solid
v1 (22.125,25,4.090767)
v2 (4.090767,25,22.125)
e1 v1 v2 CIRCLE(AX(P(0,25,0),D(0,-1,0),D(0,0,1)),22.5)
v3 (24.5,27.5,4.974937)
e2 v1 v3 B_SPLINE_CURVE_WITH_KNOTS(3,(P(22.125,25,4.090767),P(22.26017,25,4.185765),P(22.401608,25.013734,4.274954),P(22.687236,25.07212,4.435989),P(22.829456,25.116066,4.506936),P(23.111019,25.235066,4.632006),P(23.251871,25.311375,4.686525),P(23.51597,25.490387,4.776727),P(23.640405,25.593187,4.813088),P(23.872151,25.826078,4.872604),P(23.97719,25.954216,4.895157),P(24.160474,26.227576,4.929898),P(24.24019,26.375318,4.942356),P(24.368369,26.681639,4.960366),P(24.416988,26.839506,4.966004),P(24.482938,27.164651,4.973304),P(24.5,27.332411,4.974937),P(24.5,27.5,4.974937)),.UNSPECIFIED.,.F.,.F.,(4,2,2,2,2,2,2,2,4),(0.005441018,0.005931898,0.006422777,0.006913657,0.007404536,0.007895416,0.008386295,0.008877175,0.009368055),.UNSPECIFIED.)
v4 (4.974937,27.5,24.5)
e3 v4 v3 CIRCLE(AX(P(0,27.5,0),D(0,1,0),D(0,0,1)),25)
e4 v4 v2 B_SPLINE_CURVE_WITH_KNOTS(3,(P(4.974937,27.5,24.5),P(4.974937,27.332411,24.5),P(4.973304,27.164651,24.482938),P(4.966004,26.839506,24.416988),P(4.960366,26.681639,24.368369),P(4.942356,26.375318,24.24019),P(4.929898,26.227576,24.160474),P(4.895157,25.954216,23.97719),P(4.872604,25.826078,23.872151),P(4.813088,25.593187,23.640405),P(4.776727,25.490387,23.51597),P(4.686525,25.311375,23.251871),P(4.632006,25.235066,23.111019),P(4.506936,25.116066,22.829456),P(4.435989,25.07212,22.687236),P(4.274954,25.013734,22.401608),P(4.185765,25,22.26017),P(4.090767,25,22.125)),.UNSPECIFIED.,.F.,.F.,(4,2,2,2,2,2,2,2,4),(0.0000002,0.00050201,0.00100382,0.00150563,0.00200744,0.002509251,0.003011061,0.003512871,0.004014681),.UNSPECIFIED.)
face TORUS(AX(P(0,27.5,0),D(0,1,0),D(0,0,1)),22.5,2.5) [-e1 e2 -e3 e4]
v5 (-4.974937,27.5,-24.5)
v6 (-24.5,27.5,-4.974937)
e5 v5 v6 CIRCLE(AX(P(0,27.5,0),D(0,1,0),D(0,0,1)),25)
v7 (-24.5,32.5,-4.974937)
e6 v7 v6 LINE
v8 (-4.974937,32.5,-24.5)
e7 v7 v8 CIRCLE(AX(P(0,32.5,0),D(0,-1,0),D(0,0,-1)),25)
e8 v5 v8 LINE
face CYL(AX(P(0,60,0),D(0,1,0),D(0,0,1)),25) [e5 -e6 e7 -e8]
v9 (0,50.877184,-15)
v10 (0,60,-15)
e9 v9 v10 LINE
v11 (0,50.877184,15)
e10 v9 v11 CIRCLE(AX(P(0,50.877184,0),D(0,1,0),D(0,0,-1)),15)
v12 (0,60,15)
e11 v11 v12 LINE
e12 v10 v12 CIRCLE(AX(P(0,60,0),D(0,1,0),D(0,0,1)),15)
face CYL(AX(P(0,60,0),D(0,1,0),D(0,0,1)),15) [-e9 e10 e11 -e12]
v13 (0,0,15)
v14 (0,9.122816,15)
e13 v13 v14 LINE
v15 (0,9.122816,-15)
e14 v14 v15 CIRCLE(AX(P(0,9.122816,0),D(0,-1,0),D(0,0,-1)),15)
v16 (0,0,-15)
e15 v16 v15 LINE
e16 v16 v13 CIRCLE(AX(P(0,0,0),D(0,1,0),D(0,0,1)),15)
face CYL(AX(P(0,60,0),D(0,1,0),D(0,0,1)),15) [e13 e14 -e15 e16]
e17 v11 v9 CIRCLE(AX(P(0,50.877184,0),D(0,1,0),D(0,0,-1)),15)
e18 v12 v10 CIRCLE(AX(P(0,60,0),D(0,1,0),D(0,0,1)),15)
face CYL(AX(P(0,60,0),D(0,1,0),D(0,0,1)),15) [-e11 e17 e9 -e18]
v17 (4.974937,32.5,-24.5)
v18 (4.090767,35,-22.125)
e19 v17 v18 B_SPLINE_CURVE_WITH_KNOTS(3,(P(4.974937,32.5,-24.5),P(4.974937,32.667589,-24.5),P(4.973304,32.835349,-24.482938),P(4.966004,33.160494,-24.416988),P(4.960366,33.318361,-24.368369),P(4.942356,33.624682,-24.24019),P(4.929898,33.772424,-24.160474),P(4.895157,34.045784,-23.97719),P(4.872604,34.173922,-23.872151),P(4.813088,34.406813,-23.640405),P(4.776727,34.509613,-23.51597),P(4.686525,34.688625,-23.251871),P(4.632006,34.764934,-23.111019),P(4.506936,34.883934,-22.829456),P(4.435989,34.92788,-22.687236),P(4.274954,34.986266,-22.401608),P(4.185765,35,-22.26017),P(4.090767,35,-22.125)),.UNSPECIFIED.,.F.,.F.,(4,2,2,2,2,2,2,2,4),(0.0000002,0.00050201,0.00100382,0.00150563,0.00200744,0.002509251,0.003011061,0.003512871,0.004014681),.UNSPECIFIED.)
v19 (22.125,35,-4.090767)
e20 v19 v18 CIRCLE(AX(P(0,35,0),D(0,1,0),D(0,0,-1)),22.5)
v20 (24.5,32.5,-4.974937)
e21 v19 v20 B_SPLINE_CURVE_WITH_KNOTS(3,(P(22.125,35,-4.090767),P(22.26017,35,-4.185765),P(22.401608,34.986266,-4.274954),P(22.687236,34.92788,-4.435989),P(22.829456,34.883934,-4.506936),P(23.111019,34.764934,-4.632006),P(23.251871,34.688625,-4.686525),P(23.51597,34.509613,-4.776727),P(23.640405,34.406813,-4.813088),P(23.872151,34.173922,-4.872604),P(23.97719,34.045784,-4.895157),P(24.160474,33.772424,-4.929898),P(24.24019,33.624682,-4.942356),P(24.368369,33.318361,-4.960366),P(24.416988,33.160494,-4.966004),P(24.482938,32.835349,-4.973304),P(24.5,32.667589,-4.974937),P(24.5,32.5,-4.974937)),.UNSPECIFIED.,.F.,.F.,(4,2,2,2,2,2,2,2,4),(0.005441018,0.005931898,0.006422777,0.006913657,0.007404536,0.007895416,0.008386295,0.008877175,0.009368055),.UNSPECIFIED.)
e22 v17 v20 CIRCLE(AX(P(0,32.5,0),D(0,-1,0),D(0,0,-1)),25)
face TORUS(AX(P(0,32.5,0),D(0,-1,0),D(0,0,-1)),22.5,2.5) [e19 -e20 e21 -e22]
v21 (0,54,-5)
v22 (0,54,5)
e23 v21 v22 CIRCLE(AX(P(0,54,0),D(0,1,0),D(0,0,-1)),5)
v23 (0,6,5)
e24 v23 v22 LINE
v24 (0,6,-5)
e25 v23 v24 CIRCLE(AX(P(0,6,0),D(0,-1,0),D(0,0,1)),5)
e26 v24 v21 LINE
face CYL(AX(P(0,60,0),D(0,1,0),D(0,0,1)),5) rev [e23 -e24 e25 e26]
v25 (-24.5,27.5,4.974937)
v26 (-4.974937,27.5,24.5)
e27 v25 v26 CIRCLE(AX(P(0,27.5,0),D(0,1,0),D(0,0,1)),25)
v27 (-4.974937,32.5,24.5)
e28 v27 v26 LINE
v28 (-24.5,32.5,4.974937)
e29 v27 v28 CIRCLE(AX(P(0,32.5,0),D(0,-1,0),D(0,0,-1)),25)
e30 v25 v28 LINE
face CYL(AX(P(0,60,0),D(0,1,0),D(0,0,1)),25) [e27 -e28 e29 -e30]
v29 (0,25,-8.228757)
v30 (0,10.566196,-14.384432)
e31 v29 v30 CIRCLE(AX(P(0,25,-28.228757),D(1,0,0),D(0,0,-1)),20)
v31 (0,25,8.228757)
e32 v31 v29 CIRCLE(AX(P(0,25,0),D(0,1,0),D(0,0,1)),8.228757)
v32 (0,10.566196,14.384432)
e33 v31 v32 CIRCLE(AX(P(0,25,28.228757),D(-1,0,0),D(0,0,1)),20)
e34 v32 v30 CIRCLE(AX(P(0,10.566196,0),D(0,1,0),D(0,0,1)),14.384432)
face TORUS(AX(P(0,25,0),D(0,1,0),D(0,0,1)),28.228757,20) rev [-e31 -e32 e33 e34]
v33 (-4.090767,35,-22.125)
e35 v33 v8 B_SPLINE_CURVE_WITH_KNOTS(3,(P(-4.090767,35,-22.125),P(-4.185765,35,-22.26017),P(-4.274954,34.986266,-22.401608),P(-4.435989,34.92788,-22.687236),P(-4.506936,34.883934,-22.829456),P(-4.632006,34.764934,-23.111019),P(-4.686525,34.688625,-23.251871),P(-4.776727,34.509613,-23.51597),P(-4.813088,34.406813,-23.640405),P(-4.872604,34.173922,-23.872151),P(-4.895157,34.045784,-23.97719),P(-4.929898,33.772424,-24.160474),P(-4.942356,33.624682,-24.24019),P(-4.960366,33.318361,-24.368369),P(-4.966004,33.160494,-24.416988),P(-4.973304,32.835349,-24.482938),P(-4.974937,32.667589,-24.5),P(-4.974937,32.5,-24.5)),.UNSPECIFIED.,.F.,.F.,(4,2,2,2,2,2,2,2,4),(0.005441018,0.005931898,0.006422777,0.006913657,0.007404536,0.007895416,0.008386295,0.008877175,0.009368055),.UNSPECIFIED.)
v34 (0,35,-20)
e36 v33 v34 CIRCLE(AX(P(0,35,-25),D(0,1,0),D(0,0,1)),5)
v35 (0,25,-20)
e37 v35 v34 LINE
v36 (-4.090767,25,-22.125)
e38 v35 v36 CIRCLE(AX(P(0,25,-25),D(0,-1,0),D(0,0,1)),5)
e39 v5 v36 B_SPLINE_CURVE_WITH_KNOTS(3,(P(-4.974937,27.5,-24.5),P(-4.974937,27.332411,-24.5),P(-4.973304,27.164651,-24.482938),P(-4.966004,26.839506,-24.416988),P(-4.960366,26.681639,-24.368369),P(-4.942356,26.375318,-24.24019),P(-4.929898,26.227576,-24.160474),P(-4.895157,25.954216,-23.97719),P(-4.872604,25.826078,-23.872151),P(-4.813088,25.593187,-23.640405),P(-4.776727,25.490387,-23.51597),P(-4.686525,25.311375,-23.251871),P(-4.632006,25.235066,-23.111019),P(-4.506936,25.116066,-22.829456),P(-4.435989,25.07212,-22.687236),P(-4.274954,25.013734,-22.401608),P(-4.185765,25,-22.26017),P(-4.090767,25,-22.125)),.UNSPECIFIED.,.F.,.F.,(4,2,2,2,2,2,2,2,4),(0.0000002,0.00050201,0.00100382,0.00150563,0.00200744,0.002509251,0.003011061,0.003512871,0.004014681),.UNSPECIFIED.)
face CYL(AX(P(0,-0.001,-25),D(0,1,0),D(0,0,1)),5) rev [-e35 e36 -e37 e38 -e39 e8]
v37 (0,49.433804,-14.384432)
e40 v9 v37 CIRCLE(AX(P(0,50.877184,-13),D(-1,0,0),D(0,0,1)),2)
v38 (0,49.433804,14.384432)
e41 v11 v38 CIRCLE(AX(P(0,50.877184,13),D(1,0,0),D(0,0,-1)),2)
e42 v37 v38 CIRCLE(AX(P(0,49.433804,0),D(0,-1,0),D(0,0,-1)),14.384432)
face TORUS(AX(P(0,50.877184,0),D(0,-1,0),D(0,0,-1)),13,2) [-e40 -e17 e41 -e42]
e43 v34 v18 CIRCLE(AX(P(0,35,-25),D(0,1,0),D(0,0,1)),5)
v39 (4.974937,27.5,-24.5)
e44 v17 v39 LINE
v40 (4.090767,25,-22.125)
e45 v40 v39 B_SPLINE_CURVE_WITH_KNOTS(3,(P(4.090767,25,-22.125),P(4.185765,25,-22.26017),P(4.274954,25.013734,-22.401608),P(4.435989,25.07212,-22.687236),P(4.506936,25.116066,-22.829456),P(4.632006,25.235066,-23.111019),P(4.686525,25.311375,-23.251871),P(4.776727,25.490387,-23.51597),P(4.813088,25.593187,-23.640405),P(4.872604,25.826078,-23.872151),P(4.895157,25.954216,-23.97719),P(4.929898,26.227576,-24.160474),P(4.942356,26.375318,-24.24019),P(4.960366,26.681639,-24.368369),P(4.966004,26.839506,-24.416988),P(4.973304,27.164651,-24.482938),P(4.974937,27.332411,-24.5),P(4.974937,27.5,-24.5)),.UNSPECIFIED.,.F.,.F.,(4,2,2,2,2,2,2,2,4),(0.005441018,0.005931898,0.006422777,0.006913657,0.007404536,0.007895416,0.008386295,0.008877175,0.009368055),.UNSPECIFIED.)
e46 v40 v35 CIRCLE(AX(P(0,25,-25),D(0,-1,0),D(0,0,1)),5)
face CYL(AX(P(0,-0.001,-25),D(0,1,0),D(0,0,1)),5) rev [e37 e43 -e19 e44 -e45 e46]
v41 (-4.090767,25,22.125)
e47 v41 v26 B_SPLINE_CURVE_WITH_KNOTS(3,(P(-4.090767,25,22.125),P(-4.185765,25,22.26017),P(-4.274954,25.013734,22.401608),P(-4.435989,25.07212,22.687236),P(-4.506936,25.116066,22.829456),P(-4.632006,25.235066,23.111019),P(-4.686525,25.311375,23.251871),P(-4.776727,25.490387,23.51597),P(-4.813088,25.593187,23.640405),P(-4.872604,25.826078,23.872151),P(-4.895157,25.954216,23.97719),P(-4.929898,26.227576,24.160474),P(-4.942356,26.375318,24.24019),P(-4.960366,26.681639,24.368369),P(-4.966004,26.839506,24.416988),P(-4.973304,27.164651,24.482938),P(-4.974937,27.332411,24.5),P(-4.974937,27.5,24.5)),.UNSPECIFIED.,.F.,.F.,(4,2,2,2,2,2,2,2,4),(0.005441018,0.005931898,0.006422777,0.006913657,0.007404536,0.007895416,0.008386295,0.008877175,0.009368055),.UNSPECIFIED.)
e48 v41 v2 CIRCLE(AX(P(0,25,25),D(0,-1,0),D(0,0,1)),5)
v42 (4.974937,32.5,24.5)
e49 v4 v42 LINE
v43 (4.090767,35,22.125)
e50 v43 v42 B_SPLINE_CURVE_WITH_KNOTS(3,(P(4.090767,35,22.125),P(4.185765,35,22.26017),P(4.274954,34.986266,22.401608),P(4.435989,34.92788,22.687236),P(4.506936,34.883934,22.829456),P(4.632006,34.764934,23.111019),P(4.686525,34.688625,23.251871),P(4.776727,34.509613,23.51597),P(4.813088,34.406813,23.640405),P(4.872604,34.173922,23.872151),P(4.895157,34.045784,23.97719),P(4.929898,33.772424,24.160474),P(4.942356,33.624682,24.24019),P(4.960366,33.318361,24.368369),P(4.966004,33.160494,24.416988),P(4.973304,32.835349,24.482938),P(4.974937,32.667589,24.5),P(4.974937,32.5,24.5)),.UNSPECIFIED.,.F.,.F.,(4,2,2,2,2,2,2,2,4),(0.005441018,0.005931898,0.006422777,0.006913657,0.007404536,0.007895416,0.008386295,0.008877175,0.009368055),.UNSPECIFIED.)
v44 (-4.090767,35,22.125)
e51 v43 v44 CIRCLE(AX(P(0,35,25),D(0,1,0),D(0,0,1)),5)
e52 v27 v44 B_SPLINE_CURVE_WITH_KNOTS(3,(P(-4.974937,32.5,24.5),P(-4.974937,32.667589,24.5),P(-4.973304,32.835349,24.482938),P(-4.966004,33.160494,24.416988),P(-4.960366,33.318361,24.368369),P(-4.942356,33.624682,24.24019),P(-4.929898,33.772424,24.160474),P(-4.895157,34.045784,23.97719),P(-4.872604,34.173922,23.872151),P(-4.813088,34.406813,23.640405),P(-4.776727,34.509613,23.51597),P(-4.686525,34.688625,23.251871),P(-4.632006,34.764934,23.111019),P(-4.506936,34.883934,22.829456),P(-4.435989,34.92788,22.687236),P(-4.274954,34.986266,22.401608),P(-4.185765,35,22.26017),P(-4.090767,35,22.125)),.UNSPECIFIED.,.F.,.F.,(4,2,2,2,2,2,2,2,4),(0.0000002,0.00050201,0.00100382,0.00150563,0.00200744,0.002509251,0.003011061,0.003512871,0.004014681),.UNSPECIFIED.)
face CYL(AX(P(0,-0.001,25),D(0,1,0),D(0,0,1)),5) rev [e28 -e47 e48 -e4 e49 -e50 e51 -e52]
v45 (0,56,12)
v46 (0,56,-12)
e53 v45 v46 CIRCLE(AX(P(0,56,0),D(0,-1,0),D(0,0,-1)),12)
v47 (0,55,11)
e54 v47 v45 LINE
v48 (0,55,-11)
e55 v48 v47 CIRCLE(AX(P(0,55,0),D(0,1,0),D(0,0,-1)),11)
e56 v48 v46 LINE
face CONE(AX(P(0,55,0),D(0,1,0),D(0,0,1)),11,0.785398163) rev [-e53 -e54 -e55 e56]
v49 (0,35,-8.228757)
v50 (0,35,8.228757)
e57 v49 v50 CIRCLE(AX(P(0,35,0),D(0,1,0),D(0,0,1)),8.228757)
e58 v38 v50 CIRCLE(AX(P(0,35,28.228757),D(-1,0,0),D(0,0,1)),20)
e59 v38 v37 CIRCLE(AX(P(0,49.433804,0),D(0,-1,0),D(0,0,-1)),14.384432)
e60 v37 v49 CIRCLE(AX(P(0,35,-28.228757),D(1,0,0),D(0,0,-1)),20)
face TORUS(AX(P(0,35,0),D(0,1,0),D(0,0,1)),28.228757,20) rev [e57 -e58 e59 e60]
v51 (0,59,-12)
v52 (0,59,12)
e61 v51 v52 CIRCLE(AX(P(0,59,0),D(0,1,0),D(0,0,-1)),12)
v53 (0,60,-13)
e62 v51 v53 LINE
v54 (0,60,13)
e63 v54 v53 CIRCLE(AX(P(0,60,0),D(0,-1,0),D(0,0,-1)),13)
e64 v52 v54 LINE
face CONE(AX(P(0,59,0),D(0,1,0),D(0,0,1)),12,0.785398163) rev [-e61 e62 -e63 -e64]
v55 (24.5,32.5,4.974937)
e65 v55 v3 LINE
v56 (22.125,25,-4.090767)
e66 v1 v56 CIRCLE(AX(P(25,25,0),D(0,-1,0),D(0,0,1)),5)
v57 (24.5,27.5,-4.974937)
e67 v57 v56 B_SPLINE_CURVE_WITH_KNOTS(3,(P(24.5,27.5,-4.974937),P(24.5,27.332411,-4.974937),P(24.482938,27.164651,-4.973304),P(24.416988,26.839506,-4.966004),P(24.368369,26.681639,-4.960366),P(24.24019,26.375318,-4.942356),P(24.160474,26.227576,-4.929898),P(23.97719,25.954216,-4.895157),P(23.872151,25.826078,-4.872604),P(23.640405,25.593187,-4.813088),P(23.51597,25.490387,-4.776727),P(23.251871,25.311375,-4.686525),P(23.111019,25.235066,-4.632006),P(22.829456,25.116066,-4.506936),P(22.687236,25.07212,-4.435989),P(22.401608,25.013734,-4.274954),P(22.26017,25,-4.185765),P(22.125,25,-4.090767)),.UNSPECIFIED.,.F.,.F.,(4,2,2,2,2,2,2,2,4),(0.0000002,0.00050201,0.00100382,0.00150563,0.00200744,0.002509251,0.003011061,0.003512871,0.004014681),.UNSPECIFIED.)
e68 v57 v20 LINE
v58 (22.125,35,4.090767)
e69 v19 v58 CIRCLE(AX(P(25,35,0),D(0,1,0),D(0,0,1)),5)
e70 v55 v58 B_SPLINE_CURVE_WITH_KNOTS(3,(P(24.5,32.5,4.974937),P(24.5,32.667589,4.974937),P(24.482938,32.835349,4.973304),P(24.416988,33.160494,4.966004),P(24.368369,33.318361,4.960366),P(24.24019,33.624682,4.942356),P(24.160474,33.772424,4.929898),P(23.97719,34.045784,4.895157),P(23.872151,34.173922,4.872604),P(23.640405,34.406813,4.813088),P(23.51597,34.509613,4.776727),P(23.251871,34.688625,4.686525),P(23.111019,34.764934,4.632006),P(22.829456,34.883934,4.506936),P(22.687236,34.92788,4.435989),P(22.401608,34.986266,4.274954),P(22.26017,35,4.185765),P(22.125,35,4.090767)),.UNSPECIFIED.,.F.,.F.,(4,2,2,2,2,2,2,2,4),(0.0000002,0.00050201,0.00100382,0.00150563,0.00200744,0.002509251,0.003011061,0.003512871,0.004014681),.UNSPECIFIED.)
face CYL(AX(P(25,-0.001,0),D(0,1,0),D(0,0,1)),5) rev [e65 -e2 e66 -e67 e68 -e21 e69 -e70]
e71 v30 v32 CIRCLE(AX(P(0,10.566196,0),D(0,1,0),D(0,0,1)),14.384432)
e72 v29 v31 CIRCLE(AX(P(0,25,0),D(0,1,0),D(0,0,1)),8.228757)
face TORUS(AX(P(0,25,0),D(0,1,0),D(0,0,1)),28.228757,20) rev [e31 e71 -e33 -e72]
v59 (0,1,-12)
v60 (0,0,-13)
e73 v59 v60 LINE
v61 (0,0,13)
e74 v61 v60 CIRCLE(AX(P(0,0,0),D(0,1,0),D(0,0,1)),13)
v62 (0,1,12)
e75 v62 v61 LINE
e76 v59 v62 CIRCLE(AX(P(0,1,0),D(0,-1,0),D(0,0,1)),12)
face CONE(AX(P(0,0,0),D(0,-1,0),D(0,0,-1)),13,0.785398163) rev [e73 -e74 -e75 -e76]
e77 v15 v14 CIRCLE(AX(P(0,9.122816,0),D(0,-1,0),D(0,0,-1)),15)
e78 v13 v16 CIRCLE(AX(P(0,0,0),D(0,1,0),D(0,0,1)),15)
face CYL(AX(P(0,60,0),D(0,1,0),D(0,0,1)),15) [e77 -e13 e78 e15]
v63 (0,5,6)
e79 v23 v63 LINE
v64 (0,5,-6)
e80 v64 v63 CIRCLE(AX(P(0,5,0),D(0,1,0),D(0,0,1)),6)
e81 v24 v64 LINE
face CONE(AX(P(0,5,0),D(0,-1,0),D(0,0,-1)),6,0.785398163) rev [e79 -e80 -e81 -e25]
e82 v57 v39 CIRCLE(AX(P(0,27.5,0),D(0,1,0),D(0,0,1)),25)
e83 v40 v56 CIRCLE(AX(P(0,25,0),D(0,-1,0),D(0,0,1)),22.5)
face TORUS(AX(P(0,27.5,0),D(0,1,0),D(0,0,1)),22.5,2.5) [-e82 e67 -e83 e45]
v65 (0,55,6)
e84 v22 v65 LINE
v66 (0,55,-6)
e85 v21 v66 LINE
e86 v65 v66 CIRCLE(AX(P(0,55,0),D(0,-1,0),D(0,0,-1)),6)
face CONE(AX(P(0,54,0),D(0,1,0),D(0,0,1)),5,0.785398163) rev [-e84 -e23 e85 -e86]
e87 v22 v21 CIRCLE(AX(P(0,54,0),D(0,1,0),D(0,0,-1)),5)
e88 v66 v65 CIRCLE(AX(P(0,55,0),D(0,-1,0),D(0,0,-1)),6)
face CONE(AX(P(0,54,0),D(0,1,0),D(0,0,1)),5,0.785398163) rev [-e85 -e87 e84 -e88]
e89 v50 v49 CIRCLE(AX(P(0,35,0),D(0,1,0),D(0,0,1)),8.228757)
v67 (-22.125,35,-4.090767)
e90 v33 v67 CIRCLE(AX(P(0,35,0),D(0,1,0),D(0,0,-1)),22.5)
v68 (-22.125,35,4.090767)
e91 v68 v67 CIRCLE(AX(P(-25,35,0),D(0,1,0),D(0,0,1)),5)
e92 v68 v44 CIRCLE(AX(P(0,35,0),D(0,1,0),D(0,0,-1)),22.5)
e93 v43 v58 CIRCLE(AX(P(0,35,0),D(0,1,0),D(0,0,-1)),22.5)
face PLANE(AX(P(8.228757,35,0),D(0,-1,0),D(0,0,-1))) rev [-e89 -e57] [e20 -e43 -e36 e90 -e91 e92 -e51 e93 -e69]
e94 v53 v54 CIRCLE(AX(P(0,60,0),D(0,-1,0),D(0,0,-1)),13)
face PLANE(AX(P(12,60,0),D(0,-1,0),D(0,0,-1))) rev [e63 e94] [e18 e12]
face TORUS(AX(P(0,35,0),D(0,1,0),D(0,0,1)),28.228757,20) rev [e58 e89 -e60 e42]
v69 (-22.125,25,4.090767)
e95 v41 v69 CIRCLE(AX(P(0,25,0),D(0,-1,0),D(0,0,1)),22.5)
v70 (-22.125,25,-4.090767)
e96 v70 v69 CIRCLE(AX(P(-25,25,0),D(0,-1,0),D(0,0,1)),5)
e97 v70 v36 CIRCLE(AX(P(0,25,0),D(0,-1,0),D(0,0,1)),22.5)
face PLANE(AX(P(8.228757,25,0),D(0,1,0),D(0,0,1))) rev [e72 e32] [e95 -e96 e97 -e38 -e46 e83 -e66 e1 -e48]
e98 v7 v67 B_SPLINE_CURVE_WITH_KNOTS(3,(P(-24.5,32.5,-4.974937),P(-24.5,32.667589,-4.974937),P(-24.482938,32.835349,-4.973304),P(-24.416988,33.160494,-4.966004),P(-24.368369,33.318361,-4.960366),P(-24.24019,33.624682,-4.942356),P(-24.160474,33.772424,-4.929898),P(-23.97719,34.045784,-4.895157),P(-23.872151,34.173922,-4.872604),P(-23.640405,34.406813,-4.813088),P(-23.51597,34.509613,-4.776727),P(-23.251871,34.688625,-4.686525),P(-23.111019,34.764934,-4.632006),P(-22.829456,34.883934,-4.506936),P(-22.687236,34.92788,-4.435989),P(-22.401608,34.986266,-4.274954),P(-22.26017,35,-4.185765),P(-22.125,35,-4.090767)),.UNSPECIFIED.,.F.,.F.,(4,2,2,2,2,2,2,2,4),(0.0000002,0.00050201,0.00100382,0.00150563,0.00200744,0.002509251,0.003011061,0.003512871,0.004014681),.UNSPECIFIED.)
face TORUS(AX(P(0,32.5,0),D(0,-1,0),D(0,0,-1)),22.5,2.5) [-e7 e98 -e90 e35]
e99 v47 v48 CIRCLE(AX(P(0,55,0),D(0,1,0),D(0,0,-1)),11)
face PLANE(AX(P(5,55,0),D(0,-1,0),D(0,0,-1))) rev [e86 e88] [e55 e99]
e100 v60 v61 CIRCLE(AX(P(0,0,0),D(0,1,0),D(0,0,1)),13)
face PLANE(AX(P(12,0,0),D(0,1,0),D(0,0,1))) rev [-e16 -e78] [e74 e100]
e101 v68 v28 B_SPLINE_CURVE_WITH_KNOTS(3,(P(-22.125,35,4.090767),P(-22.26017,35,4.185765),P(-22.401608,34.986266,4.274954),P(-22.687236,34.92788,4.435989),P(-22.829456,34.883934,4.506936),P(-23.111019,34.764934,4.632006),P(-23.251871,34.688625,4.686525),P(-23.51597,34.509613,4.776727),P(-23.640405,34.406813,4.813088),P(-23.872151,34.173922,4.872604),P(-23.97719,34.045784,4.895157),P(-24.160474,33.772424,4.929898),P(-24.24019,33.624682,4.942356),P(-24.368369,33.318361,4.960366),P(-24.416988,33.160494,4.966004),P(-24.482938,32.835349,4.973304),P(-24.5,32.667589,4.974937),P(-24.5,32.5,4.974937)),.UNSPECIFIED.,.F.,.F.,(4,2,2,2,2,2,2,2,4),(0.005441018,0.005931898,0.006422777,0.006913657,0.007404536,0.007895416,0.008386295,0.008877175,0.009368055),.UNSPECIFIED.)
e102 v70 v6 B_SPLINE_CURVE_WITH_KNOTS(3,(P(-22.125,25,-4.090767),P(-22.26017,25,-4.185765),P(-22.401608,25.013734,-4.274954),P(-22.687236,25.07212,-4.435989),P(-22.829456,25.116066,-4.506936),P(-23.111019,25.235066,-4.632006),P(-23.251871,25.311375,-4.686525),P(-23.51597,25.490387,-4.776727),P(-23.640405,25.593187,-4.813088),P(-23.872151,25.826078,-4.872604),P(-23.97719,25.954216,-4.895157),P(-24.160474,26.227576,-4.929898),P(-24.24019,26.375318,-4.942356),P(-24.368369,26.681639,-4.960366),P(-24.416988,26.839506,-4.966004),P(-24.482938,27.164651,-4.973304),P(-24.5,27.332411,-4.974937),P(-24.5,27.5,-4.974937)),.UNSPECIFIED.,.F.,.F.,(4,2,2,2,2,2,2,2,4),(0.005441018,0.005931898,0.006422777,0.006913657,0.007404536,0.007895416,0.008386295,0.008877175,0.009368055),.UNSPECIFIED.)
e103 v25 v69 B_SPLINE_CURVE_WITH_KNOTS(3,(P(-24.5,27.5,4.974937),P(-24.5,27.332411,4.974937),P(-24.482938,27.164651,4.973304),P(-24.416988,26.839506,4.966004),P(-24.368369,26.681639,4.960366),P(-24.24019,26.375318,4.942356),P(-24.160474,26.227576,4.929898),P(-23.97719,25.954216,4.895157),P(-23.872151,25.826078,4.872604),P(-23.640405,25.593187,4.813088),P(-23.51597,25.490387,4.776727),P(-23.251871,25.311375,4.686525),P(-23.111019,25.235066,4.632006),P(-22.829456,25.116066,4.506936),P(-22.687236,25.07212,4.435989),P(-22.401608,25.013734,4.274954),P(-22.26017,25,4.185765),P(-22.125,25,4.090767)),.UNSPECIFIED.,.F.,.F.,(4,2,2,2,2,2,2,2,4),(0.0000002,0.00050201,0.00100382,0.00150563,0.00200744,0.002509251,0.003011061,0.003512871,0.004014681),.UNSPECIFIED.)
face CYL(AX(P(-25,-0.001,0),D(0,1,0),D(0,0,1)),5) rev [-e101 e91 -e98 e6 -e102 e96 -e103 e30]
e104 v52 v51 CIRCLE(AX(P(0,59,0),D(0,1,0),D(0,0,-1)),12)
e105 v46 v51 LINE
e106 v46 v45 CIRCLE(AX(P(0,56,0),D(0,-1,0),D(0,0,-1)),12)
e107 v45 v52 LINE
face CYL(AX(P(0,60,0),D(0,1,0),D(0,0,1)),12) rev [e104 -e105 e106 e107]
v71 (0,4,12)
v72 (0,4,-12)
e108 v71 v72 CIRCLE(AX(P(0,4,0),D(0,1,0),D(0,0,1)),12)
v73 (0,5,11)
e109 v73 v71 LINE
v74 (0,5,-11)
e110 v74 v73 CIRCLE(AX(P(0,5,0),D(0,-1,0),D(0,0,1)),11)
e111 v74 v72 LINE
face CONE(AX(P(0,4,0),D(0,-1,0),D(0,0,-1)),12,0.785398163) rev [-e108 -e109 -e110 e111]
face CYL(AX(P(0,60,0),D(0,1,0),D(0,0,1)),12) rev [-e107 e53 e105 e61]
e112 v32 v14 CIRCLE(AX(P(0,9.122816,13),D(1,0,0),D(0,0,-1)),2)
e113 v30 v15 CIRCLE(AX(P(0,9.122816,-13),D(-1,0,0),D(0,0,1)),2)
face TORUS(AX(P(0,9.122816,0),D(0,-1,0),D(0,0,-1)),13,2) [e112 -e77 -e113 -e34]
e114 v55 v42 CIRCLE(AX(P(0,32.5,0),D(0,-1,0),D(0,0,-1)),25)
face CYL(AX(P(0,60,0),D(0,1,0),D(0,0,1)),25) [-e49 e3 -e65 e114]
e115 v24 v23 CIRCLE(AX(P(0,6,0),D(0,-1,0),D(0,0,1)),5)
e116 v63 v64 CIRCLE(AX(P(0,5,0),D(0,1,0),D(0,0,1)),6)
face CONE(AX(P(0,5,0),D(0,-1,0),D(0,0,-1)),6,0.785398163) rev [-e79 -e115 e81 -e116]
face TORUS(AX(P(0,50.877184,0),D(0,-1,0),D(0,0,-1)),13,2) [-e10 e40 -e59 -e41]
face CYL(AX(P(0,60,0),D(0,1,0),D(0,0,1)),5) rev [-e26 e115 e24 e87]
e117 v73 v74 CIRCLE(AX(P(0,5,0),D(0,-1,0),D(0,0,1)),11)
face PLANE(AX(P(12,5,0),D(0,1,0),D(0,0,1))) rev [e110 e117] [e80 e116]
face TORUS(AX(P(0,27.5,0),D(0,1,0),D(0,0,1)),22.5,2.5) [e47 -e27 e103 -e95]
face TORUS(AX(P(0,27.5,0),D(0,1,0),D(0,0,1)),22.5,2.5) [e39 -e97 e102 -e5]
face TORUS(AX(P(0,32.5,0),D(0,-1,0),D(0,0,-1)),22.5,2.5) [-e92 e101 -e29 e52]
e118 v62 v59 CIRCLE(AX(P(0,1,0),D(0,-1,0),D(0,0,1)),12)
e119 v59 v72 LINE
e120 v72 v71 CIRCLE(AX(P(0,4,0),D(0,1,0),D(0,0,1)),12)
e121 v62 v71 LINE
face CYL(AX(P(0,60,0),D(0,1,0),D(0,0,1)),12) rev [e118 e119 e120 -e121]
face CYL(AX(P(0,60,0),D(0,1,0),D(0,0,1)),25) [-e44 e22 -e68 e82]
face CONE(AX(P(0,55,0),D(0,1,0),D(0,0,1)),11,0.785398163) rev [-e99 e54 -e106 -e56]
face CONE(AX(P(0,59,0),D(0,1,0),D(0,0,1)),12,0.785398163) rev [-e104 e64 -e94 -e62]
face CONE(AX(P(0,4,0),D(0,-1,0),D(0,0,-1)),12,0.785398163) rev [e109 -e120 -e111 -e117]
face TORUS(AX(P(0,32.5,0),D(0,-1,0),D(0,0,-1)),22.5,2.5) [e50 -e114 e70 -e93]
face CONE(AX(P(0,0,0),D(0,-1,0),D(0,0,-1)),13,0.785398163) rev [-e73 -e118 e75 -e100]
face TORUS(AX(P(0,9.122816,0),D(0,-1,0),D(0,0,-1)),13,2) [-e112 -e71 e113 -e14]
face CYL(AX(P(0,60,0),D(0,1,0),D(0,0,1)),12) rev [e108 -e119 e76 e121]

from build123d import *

# Parameters (mm, degrees)
FLANGE_FILLET_R2_5_R     = 2.5
FLANGE_NOTCHES_4X_REACH  = 51.749
FLANGE_NOTCH_SKETCH_R    = 5
EDGE_CHAMFER_1X45_A_SIZE = 1
EDGE_FILLET_R2_R         = 2
EDGE_CHAMFER_1X45_B_SIZE = 1


with BuildPart() as part:
    # Hub Profile Sketch → Hub Body Revolve (revolve)
    with BuildSketch(Plane.XY, mode=Mode.PRIVATE) as hub_body_revolve_sk:
        with BuildLine():
            Line((12, 0), (12, 5))
            Line((12, 5), (5, 5))
            Line((5, 5), (5, 55))
            Line((5, 55), (12, 55))
            Line((12, 55), (12, 60))
            Line((12, 60), (15, 60))
            Line((15, 60), (15, 50))
            ThreePointArc((15, 50), (10, 43.228756555), (8.228756555, 35))
            Line((8.228756555, 35), (25, 35))
            Line((25, 35), (25, 25))
            Line((25, 25), (8.228756555, 25))
            ThreePointArc((8.228756555, 25), (10, 16.771243445), (15, 10))
            Line((15, 10), (15, 0))
            Line((15, 0), (12, 0))
        make_face()
    revolve(hub_body_revolve_sk.sketch.rotate(Axis((0, 60, 0), (0, -1, 0)), 90), axis=Axis((0, 60, 0), (0, -1, 0)))

    # Flange Fillet R2.5
    flange_fillet_r2_5_edges = [part.edges().sort_by_distance(p)[0] for p in [
        (0, 25, -25),
        (0, 35, -25),
    ]]
    fillet(flange_fillet_r2_5_edges, radius=FLANGE_FILLET_R2_5_R)

    # Flange Notch Sketch → Flange Notches 4x (cut, up to next)
    with BuildSketch(Plane(origin=(0, 35, 0), x_dir=(1, 0, 0), z_dir=(0, 1, 0)), mode=Mode.PRIVATE) as flange_notches_4x_sk1:
        with Locations((0, 25)):
            Circle(FLANGE_NOTCH_SKETCH_R)
    flange_notches_4x_tool1 = extrude(flange_notches_4x_sk1.sketch, amount=-FLANGE_NOTCHES_4X_REACH, mode=Mode.PRIVATE) & part.part
    # Flange Notch Sketch → Flange Notches 4x (cut, up to next)
    with BuildSketch(Plane(origin=(0, 35, 0), x_dir=(1, 0, 0), z_dir=(0, 1, 0)), mode=Mode.PRIVATE) as flange_notches_4x_sk2:
        with Locations((25, 0)):
            Circle(FLANGE_NOTCH_SKETCH_R)
    flange_notches_4x_tool2 = extrude(flange_notches_4x_sk2.sketch, amount=-FLANGE_NOTCHES_4X_REACH, mode=Mode.PRIVATE) & part.part
    # Flange Notch Sketch → Flange Notches 4x (cut, up to next)
    with BuildSketch(Plane(origin=(0, 35, 0), x_dir=(1, 0, 0), z_dir=(0, 1, 0)), mode=Mode.PRIVATE) as flange_notches_4x_sk3:
        with Locations((0, -25)):
            Circle(FLANGE_NOTCH_SKETCH_R)
    flange_notches_4x_tool3 = extrude(flange_notches_4x_sk3.sketch, amount=-FLANGE_NOTCHES_4X_REACH, mode=Mode.PRIVATE) & part.part
    # Flange Notch Sketch → Flange Notches 4x (cut, up to next)
    with BuildSketch(Plane(origin=(0, 35, 0), x_dir=(1, 0, 0), z_dir=(0, 1, 0)), mode=Mode.PRIVATE) as flange_notches_4x_sk4:
        with Locations((-25, 0)):
            Circle(FLANGE_NOTCH_SKETCH_R)
    flange_notches_4x_tool4 = extrude(flange_notches_4x_sk4.sketch, amount=-FLANGE_NOTCHES_4X_REACH, mode=Mode.PRIVATE) & part.part
    add(flange_notches_4x_tool1.solids().sort_by_distance((0, 35, -25))[0], mode=Mode.SUBTRACT)
    add(flange_notches_4x_tool2.solids().sort_by_distance((25, 35, 0))[0], mode=Mode.SUBTRACT)
    add(flange_notches_4x_tool3.solids().sort_by_distance((0, 35, 25))[0], mode=Mode.SUBTRACT)
    add(flange_notches_4x_tool4.solids().sort_by_distance((-25, 35, 0))[0], mode=Mode.SUBTRACT)

    # Edge Chamfer 1x45 A
    edge_chamfer_1x45_a_edges = [part.edges().sort_by_distance(p)[0] for p in [
        (0, 60, -12),
        (0, 55, -5),
        (0, 5, -5),
        (0, 0, -12),
    ]]
    chamfer(edge_chamfer_1x45_a_edges, length=EDGE_CHAMFER_1X45_A_SIZE)

    # Edge Fillet R2
    edge_fillet_r2_edges = [part.edges().sort_by_distance(p)[0] for p in [
        (0, 10, -15),
        (0, 50, -15),
    ]]
    fillet(edge_fillet_r2_edges, radius=EDGE_FILLET_R2_R)

    # Edge Chamfer 1x45 B
    edge_chamfer_1x45_b_edges = [part.edges().sort_by_distance(p)[0] for p in [
        (0, 55, -12),
        (0, 5, -12),
    ]]
    chamfer(edge_chamfer_1x45_b_edges, length=EDGE_CHAMFER_1X45_B_SIZE)


solid = part.part
